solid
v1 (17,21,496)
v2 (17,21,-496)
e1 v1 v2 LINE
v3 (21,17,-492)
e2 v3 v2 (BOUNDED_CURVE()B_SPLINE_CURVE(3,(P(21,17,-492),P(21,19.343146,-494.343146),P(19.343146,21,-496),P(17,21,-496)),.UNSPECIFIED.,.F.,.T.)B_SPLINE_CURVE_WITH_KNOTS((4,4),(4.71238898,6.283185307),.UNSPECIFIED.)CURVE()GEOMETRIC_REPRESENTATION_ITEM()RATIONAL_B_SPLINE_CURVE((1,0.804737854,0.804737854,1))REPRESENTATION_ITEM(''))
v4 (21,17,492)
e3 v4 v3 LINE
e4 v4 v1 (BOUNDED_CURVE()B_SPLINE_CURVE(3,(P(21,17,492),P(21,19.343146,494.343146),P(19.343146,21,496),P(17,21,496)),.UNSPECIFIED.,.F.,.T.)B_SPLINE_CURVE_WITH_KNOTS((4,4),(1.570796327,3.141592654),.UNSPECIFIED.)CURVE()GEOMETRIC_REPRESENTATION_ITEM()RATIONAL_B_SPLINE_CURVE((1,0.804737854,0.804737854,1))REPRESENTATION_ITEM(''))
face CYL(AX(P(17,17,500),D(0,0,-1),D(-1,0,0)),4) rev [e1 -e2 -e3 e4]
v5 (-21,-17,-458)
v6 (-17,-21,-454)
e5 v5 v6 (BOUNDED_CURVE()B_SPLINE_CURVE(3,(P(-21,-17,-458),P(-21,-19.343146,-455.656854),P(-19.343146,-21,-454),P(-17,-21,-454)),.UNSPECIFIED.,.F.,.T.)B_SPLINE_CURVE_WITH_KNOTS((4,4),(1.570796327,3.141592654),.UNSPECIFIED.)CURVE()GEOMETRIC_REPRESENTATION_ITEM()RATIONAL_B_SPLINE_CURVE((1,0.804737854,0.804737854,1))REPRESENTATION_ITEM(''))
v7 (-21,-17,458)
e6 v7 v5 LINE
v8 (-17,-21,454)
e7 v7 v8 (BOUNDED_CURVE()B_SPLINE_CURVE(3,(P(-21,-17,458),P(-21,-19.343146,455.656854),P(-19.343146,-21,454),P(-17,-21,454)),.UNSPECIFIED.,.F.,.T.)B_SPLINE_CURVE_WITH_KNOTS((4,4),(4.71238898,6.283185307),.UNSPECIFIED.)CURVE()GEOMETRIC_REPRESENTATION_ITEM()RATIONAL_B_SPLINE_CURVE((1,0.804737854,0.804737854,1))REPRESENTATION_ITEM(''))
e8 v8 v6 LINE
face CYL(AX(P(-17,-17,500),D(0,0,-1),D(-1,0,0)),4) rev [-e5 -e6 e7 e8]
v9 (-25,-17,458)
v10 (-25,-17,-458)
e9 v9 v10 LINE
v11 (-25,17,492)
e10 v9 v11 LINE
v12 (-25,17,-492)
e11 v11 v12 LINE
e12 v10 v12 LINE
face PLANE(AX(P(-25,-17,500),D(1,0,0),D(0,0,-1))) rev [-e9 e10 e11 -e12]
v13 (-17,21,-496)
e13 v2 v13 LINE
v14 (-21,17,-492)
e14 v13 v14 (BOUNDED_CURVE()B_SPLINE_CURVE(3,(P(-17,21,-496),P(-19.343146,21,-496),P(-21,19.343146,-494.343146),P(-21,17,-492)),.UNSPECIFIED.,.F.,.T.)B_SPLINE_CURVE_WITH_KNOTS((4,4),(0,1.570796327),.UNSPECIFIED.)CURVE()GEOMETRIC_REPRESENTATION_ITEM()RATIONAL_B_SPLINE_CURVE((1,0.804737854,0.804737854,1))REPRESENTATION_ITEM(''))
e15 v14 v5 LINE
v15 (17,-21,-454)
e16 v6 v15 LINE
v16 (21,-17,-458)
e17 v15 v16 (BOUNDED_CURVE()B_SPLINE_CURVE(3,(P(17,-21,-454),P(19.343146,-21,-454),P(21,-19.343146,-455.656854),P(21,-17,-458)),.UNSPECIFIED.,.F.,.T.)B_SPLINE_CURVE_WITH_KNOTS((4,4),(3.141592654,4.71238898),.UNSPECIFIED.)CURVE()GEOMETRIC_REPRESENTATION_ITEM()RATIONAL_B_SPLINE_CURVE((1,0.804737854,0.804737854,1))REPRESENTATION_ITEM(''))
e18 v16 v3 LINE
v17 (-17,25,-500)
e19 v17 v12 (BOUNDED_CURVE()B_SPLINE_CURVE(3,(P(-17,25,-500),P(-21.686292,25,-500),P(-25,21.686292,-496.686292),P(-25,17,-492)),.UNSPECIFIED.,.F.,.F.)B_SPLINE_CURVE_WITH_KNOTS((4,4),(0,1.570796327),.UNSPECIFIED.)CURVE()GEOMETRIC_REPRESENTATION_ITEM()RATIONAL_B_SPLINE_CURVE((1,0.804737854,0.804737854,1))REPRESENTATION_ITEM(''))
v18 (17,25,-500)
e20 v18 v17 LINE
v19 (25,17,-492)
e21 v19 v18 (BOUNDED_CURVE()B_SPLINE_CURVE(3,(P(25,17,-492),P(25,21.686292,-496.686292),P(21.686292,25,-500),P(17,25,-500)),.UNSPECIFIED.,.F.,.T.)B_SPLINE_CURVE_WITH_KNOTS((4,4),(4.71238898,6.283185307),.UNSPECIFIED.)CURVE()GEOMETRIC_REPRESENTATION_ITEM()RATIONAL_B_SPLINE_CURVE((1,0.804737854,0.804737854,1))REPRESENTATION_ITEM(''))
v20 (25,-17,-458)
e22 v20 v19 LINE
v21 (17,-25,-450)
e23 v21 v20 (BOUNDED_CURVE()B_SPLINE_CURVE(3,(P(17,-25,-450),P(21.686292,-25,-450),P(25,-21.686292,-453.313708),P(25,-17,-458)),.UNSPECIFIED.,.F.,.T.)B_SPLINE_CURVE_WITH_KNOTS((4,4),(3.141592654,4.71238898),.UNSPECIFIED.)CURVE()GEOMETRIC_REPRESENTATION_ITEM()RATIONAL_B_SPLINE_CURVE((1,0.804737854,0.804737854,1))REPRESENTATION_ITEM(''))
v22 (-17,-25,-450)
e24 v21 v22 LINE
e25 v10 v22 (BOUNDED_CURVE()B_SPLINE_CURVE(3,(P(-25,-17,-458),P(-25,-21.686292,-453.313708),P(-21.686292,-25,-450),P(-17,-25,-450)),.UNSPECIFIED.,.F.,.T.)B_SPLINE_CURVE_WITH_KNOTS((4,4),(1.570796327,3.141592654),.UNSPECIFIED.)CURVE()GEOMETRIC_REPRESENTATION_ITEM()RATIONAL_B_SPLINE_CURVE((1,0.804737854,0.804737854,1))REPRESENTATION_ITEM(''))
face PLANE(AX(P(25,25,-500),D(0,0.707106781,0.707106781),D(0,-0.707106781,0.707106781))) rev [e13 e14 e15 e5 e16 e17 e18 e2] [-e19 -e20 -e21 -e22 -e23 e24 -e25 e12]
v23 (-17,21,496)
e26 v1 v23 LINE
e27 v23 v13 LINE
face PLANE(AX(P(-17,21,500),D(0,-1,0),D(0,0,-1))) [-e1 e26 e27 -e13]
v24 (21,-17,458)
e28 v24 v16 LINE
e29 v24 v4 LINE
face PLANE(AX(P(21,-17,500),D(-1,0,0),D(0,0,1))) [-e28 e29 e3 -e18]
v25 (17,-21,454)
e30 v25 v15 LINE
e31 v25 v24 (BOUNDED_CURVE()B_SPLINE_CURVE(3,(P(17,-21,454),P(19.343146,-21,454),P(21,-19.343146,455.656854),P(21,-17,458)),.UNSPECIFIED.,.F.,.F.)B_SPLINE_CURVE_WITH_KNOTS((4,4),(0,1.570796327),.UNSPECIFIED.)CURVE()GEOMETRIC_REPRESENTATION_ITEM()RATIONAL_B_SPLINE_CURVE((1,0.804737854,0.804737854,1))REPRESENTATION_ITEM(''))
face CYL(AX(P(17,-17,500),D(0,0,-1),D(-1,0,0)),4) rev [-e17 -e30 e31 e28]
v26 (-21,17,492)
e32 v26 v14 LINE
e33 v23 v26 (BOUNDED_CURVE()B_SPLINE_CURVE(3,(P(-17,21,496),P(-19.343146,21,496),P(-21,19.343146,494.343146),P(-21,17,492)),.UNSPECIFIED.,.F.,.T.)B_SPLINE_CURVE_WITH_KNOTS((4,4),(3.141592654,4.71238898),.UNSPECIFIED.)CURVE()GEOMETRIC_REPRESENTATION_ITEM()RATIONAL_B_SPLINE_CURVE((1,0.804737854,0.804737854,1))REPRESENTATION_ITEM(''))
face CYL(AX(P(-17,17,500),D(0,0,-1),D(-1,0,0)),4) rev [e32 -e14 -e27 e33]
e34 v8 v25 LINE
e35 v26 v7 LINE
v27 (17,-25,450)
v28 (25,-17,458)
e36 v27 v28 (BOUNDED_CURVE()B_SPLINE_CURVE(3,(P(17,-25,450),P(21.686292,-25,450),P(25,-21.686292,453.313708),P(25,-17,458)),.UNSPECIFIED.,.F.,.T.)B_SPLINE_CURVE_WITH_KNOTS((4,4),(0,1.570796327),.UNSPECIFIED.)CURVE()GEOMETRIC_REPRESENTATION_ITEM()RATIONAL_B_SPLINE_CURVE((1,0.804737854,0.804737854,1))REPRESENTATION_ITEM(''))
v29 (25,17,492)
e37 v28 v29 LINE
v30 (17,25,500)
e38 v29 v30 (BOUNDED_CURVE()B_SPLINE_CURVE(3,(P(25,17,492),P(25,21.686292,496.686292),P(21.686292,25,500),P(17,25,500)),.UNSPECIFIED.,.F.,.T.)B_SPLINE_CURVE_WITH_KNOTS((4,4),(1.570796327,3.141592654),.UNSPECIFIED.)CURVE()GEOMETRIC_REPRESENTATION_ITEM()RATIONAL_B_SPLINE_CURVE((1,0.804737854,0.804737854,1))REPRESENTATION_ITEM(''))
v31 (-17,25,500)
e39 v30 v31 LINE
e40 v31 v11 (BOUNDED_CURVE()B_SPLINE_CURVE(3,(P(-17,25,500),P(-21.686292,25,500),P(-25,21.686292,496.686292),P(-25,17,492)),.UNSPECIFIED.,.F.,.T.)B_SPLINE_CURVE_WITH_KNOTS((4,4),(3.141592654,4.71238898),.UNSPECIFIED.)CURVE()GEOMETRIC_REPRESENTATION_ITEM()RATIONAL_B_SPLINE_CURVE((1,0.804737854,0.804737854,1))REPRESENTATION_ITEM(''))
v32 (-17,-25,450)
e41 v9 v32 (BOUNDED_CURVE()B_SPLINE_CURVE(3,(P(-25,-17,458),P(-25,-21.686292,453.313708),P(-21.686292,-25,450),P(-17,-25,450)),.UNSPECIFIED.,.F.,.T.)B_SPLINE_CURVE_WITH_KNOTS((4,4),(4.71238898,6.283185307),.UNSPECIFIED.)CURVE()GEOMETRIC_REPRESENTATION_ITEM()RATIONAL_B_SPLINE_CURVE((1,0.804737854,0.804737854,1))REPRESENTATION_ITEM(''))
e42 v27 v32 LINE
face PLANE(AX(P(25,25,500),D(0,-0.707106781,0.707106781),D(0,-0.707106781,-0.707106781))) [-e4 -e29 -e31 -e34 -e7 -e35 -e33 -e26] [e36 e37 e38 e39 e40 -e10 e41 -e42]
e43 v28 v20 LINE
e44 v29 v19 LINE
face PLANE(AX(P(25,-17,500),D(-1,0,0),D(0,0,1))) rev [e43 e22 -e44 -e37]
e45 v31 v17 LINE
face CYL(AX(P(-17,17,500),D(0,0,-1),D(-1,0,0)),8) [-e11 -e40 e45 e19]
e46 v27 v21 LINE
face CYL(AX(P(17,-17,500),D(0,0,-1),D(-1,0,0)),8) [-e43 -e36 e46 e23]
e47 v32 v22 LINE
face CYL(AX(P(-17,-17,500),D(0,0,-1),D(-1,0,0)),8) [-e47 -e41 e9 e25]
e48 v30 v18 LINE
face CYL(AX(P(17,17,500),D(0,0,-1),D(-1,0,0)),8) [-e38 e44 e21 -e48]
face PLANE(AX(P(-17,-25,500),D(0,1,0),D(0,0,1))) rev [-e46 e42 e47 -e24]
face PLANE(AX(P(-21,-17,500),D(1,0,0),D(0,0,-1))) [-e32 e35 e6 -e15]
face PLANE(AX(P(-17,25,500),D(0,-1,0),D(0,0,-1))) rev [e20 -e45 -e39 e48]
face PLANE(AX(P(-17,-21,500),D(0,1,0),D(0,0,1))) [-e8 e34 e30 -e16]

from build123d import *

# Parameters (mm, degrees)
BOSS_EXTRUDE1_DEPTH = 500
CUT_EXTRUDE1_DEPTH  = 504.115294937


with BuildPart() as part:
    # Sketch1 → Boss-Extrude1 (new, symmetric)
    with BuildSketch(Plane.XY):
        with BuildLine():
            Line((-17, -25), (17, -25))
            ThreePointArc((17, -25), (22.656854249, -22.656854249), (25, -17))
            Line((25, -17), (25, 17))
            ThreePointArc((25, 17), (22.656854249, 22.656854249), (17, 25))
            Line((17, 25), (-17, 25))
            ThreePointArc((-17, 25), (-22.656854249, 22.656854249), (-25, 17))
            Line((-25, 17), (-25, -17))
            ThreePointArc((-25, -17), (-22.656854249, -22.656854249), (-17, -25))
        make_face()
        with BuildLine():
            Line((-17, 21), (17, 21))
            ThreePointArc((17, 21), (19.828427125, 19.828427125), (21, 17))
            Line((21, 17), (21, -17))
            ThreePointArc((21, -17), (19.828427125, -19.828427125), (17, -21))
            Line((17, -21), (-17, -21))
            ThreePointArc((-17, -21), (-19.828427125, -19.828427125), (-21, -17))
            Line((-21, -17), (-21, 17))
            ThreePointArc((-21, 17), (-19.828427125, 19.828427125), (-17, 21))
        make_face(mode=Mode.SUBTRACT)
    extrude(amount=BOSS_EXTRUDE1_DEPTH, both=True)

    # Sketch2 → Cut-Extrude1 (cut, through all)
    with BuildSketch(Plane.ZY.offset(25)):
        Polygon((-500, 25), (-450, -25), (-500, -25), align=None)
    cut_extrude1 = extrude(amount=-CUT_EXTRUDE1_DEPTH, mode=Mode.SUBTRACT)

    # Mirror1: Cut-Extrude1 across plane
    add(cut_extrude1.mirror(Plane.XY), mode=Mode.SUBTRACT)


solid = part.part
